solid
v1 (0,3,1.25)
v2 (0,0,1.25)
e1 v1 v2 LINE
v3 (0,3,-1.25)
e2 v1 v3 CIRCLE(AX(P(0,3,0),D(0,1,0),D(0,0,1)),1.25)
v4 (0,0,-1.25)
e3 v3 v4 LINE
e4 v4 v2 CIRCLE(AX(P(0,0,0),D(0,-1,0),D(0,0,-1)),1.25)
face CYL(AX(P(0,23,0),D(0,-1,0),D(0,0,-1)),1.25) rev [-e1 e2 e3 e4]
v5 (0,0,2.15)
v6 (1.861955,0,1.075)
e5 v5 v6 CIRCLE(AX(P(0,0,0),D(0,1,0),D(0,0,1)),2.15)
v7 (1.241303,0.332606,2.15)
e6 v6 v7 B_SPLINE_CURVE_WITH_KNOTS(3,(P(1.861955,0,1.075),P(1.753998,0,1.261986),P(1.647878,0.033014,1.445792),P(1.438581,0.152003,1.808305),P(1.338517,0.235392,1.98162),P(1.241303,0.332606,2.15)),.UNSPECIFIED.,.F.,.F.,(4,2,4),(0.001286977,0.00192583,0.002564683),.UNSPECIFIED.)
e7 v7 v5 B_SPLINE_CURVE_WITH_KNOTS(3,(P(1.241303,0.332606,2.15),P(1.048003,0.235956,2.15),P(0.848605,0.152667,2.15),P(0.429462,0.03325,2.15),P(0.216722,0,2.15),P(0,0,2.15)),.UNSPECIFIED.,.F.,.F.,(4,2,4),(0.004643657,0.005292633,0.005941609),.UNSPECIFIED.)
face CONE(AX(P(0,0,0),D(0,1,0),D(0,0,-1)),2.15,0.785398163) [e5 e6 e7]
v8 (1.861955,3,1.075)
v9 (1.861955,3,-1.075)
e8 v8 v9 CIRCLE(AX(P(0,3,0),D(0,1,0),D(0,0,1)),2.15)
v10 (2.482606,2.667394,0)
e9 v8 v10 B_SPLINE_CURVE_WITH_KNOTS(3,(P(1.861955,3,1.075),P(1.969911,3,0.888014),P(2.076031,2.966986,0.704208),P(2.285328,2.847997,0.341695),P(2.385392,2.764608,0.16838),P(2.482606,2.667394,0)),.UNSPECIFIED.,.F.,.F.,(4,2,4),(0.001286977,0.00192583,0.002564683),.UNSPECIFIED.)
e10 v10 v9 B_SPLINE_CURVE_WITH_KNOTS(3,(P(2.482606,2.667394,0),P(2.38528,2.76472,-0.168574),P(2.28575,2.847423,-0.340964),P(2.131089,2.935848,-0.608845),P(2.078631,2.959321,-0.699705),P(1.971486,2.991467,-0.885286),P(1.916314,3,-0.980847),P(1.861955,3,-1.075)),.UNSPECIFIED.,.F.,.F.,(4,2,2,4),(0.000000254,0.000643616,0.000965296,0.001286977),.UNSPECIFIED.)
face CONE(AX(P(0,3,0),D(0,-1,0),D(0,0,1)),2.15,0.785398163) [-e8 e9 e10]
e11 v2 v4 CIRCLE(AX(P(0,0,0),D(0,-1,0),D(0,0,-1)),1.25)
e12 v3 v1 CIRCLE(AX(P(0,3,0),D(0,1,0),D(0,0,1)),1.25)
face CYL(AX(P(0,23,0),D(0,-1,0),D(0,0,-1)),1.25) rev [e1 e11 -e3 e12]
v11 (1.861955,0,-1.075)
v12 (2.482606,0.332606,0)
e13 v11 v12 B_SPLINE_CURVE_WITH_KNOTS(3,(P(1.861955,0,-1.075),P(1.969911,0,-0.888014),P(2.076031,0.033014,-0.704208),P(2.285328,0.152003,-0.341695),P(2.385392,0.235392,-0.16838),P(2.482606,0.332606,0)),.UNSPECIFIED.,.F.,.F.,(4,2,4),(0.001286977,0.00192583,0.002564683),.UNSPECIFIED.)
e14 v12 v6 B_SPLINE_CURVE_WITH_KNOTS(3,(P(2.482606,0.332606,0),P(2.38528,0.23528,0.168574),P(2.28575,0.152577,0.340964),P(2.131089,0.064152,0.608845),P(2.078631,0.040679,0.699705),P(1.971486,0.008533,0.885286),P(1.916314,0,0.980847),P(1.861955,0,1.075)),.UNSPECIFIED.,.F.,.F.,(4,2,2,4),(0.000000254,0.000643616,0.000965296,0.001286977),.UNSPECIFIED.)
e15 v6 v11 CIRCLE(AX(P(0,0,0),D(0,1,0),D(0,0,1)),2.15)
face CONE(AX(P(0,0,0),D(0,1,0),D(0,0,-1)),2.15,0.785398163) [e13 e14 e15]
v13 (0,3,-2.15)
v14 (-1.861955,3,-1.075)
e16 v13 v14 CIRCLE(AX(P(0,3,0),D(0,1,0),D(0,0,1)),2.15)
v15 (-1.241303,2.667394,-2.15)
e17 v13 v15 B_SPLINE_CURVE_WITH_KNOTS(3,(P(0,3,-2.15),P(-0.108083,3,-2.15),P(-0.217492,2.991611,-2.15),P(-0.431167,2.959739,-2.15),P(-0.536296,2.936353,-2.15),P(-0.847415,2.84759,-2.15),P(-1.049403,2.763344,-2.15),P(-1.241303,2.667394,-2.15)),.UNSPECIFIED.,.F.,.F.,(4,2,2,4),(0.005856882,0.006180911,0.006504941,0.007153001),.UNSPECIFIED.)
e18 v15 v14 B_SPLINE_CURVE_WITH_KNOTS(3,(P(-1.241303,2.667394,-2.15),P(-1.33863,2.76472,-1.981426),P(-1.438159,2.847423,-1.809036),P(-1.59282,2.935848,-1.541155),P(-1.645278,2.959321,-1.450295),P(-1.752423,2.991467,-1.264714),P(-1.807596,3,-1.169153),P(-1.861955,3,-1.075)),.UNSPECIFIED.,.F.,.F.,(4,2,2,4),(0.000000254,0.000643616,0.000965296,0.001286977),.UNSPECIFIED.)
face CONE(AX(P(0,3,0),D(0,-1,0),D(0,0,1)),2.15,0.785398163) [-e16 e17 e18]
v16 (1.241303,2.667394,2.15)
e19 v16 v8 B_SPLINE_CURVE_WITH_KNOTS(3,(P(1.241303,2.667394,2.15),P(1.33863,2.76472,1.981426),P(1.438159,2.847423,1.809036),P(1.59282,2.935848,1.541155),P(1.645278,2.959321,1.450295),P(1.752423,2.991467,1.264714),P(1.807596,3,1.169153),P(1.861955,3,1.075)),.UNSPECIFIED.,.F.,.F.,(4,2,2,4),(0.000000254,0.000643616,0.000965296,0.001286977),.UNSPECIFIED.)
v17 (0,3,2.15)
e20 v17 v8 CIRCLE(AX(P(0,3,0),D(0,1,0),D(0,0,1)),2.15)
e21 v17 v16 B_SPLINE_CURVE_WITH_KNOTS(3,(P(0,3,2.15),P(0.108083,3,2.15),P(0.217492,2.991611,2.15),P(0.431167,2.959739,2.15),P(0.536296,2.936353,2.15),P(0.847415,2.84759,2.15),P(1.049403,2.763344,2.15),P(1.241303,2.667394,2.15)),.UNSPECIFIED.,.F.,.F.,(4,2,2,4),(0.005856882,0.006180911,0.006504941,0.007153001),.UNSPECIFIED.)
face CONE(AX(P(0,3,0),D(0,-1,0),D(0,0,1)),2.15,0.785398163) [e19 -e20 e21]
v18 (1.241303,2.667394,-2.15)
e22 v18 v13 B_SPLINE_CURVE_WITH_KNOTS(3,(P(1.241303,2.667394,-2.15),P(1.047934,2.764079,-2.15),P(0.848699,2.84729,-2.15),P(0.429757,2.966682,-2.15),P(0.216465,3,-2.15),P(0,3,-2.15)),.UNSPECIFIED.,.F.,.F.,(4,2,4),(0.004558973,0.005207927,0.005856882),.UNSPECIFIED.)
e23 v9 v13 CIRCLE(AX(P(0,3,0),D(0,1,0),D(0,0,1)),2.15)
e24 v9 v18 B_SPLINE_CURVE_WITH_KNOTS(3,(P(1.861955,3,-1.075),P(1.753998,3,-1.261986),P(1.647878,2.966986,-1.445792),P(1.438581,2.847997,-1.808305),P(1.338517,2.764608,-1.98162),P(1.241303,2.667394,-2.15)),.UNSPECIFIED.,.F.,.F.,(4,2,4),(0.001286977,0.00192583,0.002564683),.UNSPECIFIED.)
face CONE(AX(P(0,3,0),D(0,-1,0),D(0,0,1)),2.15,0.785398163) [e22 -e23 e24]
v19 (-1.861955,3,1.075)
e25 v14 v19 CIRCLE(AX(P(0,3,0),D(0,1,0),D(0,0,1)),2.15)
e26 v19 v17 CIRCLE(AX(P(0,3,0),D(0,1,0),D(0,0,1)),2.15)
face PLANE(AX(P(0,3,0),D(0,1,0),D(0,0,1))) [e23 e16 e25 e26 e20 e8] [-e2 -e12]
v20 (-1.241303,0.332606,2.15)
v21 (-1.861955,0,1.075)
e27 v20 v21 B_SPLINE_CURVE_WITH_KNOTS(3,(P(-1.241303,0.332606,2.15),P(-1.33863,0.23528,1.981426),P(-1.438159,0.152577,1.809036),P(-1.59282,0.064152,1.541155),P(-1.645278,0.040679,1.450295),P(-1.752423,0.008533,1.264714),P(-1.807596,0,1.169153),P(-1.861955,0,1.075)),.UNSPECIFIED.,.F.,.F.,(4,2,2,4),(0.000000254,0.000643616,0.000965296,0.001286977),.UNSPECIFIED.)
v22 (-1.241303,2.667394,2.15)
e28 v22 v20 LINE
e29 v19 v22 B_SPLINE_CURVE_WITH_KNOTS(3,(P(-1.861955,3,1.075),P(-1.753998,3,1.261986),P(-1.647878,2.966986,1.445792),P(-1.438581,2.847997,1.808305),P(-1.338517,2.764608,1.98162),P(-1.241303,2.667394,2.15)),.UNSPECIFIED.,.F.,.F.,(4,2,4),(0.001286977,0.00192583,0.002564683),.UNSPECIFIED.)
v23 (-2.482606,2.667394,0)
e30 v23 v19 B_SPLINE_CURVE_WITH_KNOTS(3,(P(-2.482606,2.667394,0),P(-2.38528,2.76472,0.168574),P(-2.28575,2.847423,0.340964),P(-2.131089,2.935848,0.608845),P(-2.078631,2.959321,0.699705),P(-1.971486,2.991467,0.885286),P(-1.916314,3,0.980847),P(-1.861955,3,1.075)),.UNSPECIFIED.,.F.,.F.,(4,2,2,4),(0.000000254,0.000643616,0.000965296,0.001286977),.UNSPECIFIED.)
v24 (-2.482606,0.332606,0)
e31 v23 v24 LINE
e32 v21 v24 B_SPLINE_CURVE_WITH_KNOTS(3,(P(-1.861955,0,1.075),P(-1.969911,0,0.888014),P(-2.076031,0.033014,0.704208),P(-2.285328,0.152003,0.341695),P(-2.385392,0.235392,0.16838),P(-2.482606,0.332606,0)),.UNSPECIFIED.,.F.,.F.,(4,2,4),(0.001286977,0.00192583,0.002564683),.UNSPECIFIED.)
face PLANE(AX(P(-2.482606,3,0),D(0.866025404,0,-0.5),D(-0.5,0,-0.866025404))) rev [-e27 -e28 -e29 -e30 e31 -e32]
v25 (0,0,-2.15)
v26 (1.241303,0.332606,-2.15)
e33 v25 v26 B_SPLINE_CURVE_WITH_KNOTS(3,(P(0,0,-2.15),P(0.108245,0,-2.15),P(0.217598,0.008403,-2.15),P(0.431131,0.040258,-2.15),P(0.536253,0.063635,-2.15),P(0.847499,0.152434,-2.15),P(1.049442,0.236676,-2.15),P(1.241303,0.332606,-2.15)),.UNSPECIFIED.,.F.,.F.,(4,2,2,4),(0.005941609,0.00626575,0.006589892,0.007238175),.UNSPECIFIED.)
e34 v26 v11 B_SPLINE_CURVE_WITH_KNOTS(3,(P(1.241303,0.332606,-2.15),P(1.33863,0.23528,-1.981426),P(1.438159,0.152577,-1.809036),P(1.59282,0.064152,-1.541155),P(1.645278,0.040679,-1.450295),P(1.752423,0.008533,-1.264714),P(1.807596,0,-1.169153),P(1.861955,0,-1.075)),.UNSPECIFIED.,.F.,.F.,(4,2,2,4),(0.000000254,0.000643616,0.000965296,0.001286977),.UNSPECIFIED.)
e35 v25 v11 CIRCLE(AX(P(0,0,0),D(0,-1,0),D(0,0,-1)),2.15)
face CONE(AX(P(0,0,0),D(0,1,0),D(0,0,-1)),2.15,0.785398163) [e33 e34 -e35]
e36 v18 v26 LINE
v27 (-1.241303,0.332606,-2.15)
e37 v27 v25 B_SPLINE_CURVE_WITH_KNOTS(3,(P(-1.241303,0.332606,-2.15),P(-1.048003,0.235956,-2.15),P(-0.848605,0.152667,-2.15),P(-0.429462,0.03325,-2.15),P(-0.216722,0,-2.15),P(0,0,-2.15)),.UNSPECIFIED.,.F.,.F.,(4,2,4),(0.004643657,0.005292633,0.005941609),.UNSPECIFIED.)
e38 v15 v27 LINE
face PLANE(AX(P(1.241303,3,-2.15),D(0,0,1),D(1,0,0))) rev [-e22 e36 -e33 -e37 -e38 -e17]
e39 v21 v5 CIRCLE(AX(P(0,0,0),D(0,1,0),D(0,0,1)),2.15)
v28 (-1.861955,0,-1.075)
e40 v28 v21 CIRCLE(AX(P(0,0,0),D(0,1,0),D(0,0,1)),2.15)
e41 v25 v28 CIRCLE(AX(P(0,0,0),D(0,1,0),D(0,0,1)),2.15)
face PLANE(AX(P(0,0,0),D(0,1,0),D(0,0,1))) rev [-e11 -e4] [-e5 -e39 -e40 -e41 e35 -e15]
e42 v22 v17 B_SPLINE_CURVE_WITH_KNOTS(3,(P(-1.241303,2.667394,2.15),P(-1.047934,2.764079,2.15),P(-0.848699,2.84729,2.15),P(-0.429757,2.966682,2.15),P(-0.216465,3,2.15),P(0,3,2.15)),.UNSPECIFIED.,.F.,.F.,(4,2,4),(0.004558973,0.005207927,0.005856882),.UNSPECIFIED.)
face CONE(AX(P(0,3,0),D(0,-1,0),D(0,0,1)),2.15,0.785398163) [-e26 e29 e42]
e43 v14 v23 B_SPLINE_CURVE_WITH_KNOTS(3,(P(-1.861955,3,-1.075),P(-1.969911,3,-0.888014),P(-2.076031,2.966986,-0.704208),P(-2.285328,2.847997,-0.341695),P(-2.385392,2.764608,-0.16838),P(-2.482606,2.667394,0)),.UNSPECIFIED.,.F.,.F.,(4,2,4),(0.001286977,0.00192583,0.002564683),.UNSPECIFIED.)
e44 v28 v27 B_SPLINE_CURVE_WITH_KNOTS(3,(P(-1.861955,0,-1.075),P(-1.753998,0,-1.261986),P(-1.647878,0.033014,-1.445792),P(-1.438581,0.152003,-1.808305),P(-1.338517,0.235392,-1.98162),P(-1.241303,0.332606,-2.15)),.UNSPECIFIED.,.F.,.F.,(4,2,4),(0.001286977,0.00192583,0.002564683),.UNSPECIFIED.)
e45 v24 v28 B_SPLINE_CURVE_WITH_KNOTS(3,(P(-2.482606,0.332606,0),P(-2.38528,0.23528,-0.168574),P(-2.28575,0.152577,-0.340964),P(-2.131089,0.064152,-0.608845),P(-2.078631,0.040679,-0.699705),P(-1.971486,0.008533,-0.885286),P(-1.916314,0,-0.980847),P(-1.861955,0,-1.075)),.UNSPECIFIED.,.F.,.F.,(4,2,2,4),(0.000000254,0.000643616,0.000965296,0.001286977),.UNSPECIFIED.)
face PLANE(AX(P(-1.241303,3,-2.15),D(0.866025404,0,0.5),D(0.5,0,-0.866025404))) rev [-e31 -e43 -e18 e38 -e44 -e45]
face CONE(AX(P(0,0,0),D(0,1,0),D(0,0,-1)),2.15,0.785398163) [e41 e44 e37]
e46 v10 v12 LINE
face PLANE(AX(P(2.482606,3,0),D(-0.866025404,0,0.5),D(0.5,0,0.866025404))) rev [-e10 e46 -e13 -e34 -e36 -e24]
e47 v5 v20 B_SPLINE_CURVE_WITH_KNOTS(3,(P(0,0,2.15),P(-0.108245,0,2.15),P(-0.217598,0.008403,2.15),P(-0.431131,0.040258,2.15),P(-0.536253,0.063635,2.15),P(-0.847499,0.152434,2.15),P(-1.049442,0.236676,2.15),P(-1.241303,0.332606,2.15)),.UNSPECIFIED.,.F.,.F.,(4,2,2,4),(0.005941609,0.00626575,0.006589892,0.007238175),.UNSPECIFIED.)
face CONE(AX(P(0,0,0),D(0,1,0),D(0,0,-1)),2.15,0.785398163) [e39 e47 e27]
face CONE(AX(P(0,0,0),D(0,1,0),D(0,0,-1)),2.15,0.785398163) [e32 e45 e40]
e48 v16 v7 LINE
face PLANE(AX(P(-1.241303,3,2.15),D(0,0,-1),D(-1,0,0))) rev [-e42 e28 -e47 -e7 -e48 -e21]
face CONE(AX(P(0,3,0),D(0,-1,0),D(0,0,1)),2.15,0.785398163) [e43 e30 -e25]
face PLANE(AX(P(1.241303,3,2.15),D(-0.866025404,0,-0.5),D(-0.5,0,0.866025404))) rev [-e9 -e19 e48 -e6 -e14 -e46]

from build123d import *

# Parameters (mm, degrees)
HEX_BODY_3MM_DEPTH              = 3
FACE_CHAMFER_A_SKETCH_OUTSIDE_W = 14.41
FACE_CHAMFER_A_SKETCH_OUTSIDE_H = 13.744
FACE_CHAMFER_A_SKETCH_OUTSIDE_R = 2.15
FACE_CHAMFER_A_45DEG_DEPTH      = 3
FACE_CHAMFER_A_45DEG_DRAFT      = -45
FACE_CHAMFER_B_SKETCH_OUTSIDE_W = 14.41
FACE_CHAMFER_B_SKETCH_OUTSIDE_H = 13.744
FACE_CHAMFER_B_SKETCH_OUTSIDE_R = 2.15
FACE_CHAMFER_B_45DEG_DEPTH      = 3
FACE_CHAMFER_B_45DEG_DRAFT      = -45
BORE_2_5_SKETCH_R               = 1.25
THROUGH_BORE_2_5_DEPTH          = 23


with BuildPart() as part:
    # Hex Profile 4.3AF Sketch → Hex Body 3mm (new body)
    with BuildSketch(Plane(origin=(0, 0, 0), x_dir=(1, 0, 0), z_dir=(0, 1, 0))):
        Polygon((1.241303079, -2.15), (2.482606158, 0), (1.241303079, 2.15), (-1.241303079, 2.15), (-2.482606158, 0), (-1.241303079, -2.15), align=None)
    extrude(amount=HEX_BODY_3MM_DEPTH)


with BuildPart() as face_chamfer_a_45deg_tool:
    # Face Chamfer A Sketch outside → Face Chamfer A 45deg (with draft: the straight prism first)
    with BuildSketch(Plane(origin=(0, 3, 0), x_dir=(1, 0, 0), z_dir=(0, 1, 0))):
        Rectangle(FACE_CHAMFER_A_SKETCH_OUTSIDE_W, FACE_CHAMFER_A_SKETCH_OUTSIDE_H)
        Circle(FACE_CHAMFER_A_SKETCH_OUTSIDE_R, mode=Mode.SUBTRACT)
    extrude(amount=-FACE_CHAMFER_A_45DEG_DEPTH)
    # Face Chamfer A 45deg: the draft: its side faces are tilted about the plane it starts from
    face_chamfer_a_45deg_sides = [face_chamfer_a_45deg_tool.faces().sort_by_distance(p)[0] for p in [
        (0, 1.5, 6.872),
        (7.205, 1.5, 0),
        (0, 1.5, -6.872),
        (-7.205, 1.5, 0),
        (-2.15, 1.5, 0),
    ]]
    draft(face_chamfer_a_45deg_sides, Plane(origin=(0, 3, 0), x_dir=(1, 0, 0), z_dir=(0, 1, 0)), FACE_CHAMFER_A_45DEG_DRAFT)


with BuildPart() as part_1:
    add(part.part)

    # Face Chamfer A 45deg: cut by face_chamfer_a_45deg_tool
    add(face_chamfer_a_45deg_tool.part, mode=Mode.SUBTRACT)


with BuildPart() as face_chamfer_b_45deg_tool:
    # Face Chamfer B Sketch outside → Face Chamfer B 45deg (with draft: the straight prism first)
    with BuildSketch(Plane.XZ):
        Rectangle(FACE_CHAMFER_B_SKETCH_OUTSIDE_W, FACE_CHAMFER_B_SKETCH_OUTSIDE_H)
        Circle(FACE_CHAMFER_B_SKETCH_OUTSIDE_R, mode=Mode.SUBTRACT)
    extrude(amount=-FACE_CHAMFER_B_45DEG_DEPTH)
    # Face Chamfer B 45deg: the draft: its side faces are tilted about the plane it starts from
    face_chamfer_b_45deg_sides = [face_chamfer_b_45deg_tool.faces().sort_by_distance(p)[0] for p in [
        (0, 1.5, -6.872),
        (7.205, 1.5, 0),
        (0, 1.5, 6.872),
        (-7.205, 1.5, 0),
        (-2.15, 1.5, 0),
    ]]
    draft(face_chamfer_b_45deg_sides, Plane.XZ, FACE_CHAMFER_B_45DEG_DRAFT)


with BuildPart() as part_2:
    add(part_1.part)

    # Face Chamfer B 45deg: cut by face_chamfer_b_45deg_tool
    add(face_chamfer_b_45deg_tool.part, mode=Mode.SUBTRACT)

    # Bore Ø2.5 Sketch → Through Bore Ø2.5 (cut)
    with BuildSketch(Plane.XZ):
        with Locations(Location((0, 0, 0), (0, 0, 270))):
            Circle(BORE_2_5_SKETCH_R)
    extrude(amount=-THROUGH_BORE_2_5_DEPTH, mode=Mode.SUBTRACT)


solid = part_2.part
